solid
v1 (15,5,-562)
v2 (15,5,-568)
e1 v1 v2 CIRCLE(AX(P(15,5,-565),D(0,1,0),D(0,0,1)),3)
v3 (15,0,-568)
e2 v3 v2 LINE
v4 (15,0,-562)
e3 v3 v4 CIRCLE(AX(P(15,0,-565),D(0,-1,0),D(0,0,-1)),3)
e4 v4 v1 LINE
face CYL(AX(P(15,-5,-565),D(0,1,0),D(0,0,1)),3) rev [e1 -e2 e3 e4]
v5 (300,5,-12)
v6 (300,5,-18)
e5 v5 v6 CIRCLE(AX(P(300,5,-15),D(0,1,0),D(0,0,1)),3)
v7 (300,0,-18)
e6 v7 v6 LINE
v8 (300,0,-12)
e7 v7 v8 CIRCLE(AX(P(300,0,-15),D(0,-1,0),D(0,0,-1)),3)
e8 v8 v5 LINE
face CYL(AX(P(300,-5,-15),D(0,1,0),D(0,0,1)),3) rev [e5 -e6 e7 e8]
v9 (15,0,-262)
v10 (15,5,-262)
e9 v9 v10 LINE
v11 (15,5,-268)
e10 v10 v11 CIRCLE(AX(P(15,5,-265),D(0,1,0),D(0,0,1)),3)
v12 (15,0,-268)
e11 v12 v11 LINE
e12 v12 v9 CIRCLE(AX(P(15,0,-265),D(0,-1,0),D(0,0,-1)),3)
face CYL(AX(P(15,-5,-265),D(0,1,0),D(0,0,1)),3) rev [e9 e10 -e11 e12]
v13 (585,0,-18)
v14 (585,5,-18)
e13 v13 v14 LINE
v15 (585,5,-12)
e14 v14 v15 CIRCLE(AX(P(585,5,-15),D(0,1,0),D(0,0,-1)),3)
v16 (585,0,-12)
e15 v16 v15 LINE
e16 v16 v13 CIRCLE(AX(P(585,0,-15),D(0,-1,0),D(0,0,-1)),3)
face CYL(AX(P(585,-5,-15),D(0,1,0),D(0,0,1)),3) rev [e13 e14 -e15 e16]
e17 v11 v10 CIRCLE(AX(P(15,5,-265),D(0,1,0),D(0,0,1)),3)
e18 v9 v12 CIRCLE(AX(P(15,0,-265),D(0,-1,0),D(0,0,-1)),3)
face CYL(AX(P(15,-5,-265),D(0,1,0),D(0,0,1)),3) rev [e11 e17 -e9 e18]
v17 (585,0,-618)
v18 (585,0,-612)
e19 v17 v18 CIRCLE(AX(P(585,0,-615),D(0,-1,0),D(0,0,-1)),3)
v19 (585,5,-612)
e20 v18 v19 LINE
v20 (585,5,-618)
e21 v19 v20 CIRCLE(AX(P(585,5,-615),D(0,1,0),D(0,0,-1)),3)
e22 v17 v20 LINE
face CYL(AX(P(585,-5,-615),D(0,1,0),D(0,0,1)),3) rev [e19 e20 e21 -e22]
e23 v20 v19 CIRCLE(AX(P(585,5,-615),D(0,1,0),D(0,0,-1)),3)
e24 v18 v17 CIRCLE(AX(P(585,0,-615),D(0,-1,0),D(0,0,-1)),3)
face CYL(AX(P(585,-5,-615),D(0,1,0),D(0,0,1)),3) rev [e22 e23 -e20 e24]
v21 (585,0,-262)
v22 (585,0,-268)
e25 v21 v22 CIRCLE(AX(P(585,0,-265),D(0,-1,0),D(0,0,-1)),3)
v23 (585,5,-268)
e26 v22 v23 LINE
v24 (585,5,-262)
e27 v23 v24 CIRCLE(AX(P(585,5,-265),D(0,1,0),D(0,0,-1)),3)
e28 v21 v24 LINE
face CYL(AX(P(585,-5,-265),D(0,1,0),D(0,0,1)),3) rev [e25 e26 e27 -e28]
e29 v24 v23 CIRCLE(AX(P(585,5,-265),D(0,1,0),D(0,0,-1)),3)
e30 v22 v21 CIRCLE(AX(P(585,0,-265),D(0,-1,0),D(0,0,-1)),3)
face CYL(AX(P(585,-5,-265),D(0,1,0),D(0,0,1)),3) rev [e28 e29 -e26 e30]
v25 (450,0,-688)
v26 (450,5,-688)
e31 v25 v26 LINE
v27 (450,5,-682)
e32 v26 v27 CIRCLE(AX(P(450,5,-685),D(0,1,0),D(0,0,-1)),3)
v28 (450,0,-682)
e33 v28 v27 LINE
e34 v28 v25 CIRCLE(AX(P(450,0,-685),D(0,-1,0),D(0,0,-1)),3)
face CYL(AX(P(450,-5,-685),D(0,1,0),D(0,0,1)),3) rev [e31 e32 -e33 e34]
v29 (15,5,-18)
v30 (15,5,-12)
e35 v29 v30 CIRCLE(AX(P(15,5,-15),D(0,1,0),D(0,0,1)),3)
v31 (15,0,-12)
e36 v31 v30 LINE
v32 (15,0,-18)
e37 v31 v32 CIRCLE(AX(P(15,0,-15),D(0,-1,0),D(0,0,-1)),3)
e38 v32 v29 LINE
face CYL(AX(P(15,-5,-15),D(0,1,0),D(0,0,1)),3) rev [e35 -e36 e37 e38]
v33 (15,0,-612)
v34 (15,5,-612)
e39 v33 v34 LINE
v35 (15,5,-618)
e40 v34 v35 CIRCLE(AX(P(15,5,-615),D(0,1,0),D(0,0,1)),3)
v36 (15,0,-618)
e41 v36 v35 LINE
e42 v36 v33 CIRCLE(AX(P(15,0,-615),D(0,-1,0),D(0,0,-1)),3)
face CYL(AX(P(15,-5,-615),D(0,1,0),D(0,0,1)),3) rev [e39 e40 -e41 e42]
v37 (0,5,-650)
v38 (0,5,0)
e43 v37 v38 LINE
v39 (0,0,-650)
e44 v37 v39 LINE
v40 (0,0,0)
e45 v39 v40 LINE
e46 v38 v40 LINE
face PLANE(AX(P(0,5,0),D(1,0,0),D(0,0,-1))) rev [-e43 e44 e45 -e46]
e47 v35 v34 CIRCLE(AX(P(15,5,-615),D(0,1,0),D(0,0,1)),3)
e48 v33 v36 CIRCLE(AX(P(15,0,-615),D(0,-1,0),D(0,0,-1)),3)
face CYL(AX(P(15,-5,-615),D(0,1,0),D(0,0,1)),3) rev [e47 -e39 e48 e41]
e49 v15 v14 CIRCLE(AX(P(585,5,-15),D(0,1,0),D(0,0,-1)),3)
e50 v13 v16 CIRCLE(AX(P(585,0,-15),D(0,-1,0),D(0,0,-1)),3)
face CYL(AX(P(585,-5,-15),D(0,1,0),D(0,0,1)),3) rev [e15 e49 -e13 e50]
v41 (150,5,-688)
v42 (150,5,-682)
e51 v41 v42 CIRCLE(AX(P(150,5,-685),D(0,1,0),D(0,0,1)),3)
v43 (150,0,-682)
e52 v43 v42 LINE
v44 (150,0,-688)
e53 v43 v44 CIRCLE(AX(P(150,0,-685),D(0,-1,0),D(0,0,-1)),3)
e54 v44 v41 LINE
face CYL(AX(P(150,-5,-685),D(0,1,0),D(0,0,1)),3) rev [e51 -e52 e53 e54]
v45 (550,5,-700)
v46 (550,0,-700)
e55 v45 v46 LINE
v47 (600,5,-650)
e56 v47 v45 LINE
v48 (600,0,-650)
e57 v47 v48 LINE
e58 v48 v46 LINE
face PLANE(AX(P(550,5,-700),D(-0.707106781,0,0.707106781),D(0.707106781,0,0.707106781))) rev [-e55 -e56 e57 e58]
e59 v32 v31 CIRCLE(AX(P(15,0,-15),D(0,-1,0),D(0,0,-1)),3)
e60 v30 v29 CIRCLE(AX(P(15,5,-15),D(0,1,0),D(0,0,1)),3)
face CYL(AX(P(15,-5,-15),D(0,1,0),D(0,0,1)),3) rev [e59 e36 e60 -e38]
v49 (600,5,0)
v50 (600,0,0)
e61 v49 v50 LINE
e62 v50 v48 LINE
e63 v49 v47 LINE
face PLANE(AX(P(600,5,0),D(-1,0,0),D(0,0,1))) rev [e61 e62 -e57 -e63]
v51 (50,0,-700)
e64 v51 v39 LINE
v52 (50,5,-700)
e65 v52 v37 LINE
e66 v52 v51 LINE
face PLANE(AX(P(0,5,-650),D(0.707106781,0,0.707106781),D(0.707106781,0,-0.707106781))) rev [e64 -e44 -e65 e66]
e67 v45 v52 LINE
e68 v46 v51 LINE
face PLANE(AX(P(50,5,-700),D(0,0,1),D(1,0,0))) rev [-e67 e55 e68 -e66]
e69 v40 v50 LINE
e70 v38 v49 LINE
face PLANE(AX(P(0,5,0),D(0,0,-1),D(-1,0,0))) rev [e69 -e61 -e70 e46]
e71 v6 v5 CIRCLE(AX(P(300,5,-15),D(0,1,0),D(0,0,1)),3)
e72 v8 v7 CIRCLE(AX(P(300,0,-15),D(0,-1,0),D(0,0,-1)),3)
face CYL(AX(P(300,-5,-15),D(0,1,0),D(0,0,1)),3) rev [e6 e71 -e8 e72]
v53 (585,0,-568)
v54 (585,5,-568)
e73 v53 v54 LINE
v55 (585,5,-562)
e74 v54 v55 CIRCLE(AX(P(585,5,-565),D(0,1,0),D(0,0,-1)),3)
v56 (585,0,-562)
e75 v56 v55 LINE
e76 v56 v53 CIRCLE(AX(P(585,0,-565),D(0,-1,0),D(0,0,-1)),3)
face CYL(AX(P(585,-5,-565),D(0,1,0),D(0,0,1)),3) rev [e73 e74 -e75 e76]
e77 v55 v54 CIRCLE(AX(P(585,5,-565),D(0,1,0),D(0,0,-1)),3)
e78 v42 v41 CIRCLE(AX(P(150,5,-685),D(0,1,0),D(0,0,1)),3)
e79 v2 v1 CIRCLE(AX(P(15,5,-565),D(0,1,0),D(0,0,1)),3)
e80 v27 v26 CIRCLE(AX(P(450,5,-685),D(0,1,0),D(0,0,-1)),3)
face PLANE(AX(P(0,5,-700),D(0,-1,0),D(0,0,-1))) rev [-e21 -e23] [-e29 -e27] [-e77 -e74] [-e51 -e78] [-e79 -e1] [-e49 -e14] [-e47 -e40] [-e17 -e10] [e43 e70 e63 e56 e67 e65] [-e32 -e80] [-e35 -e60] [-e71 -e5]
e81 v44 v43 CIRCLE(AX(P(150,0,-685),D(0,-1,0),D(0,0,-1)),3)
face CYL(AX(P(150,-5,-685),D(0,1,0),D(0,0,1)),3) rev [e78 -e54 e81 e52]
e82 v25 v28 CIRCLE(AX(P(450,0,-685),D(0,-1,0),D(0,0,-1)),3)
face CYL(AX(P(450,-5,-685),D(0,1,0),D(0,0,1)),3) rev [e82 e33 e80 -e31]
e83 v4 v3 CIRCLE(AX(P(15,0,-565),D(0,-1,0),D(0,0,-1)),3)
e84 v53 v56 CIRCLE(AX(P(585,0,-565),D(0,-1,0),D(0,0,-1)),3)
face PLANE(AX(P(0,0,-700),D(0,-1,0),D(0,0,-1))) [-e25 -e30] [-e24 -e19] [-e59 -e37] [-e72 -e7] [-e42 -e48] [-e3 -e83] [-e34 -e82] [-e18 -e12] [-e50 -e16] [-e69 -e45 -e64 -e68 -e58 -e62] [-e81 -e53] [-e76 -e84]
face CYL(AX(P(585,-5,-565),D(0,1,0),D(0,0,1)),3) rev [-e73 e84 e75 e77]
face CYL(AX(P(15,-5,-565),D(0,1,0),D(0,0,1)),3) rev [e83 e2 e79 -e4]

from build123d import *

# Parameters (mm, degrees)
EXTRUDE_1_DEPTH     = 5
SKETCH_2_R          = 3
CUT_EXTRUDE_1_DEPTH = 10


with BuildPart() as part:
    # 草图1 → 凸台-拉伸1 (new body)
    with BuildSketch(Plane(origin=(0, 0, 0), x_dir=(1, 0, 0), z_dir=(0, 1, 0))):
        Polygon((0, 650), (50, 700), (550, 700), (600, 650), (600, 0), (0, 0), align=None)
    extrude(amount=EXTRUDE_1_DEPTH)

    # 草图2 → 切除-拉伸1 (cut)
    with BuildSketch(Plane(origin=(0, 5, 0), x_dir=(1, 0, 0), z_dir=(0, 1, 0))):
        with Locations(Location((15, 15, 0), (0, 0, 270))):
            Circle(SKETCH_2_R)
        with Locations(Location((15, 265, 0), (0, 0, 270))):
            Circle(SKETCH_2_R)
        with Locations(Location((15, 565, 0), (0, 0, 270))):
            Circle(SKETCH_2_R)
        with Locations(Location((15, 615, 0), (0, 0, 270))):
            Circle(SKETCH_2_R)
        with Locations(Location((150, 685, 0), (0, 0, 270))):
            Circle(SKETCH_2_R)
        with Locations(Location((585, 15, 0), (0, 0, 90))):
            Circle(SKETCH_2_R)
        with Locations(Location((585, 265, 0), (0, 0, 90))):
            Circle(SKETCH_2_R)
        with Locations(Location((585, 565, 0), (0, 0, 90))):
            Circle(SKETCH_2_R)
        with Locations(Location((585, 615, 0), (0, 0, 90))):
            Circle(SKETCH_2_R)
        with Locations(Location((450, 685, 0), (0, 0, 90))):
            Circle(SKETCH_2_R)
        with Locations(Location((300, 15, 0), (0, 0, 270))):
            Circle(SKETCH_2_R)
    extrude(amount=-CUT_EXTRUDE_1_DEPTH, mode=Mode.SUBTRACT)


solid = part.part
